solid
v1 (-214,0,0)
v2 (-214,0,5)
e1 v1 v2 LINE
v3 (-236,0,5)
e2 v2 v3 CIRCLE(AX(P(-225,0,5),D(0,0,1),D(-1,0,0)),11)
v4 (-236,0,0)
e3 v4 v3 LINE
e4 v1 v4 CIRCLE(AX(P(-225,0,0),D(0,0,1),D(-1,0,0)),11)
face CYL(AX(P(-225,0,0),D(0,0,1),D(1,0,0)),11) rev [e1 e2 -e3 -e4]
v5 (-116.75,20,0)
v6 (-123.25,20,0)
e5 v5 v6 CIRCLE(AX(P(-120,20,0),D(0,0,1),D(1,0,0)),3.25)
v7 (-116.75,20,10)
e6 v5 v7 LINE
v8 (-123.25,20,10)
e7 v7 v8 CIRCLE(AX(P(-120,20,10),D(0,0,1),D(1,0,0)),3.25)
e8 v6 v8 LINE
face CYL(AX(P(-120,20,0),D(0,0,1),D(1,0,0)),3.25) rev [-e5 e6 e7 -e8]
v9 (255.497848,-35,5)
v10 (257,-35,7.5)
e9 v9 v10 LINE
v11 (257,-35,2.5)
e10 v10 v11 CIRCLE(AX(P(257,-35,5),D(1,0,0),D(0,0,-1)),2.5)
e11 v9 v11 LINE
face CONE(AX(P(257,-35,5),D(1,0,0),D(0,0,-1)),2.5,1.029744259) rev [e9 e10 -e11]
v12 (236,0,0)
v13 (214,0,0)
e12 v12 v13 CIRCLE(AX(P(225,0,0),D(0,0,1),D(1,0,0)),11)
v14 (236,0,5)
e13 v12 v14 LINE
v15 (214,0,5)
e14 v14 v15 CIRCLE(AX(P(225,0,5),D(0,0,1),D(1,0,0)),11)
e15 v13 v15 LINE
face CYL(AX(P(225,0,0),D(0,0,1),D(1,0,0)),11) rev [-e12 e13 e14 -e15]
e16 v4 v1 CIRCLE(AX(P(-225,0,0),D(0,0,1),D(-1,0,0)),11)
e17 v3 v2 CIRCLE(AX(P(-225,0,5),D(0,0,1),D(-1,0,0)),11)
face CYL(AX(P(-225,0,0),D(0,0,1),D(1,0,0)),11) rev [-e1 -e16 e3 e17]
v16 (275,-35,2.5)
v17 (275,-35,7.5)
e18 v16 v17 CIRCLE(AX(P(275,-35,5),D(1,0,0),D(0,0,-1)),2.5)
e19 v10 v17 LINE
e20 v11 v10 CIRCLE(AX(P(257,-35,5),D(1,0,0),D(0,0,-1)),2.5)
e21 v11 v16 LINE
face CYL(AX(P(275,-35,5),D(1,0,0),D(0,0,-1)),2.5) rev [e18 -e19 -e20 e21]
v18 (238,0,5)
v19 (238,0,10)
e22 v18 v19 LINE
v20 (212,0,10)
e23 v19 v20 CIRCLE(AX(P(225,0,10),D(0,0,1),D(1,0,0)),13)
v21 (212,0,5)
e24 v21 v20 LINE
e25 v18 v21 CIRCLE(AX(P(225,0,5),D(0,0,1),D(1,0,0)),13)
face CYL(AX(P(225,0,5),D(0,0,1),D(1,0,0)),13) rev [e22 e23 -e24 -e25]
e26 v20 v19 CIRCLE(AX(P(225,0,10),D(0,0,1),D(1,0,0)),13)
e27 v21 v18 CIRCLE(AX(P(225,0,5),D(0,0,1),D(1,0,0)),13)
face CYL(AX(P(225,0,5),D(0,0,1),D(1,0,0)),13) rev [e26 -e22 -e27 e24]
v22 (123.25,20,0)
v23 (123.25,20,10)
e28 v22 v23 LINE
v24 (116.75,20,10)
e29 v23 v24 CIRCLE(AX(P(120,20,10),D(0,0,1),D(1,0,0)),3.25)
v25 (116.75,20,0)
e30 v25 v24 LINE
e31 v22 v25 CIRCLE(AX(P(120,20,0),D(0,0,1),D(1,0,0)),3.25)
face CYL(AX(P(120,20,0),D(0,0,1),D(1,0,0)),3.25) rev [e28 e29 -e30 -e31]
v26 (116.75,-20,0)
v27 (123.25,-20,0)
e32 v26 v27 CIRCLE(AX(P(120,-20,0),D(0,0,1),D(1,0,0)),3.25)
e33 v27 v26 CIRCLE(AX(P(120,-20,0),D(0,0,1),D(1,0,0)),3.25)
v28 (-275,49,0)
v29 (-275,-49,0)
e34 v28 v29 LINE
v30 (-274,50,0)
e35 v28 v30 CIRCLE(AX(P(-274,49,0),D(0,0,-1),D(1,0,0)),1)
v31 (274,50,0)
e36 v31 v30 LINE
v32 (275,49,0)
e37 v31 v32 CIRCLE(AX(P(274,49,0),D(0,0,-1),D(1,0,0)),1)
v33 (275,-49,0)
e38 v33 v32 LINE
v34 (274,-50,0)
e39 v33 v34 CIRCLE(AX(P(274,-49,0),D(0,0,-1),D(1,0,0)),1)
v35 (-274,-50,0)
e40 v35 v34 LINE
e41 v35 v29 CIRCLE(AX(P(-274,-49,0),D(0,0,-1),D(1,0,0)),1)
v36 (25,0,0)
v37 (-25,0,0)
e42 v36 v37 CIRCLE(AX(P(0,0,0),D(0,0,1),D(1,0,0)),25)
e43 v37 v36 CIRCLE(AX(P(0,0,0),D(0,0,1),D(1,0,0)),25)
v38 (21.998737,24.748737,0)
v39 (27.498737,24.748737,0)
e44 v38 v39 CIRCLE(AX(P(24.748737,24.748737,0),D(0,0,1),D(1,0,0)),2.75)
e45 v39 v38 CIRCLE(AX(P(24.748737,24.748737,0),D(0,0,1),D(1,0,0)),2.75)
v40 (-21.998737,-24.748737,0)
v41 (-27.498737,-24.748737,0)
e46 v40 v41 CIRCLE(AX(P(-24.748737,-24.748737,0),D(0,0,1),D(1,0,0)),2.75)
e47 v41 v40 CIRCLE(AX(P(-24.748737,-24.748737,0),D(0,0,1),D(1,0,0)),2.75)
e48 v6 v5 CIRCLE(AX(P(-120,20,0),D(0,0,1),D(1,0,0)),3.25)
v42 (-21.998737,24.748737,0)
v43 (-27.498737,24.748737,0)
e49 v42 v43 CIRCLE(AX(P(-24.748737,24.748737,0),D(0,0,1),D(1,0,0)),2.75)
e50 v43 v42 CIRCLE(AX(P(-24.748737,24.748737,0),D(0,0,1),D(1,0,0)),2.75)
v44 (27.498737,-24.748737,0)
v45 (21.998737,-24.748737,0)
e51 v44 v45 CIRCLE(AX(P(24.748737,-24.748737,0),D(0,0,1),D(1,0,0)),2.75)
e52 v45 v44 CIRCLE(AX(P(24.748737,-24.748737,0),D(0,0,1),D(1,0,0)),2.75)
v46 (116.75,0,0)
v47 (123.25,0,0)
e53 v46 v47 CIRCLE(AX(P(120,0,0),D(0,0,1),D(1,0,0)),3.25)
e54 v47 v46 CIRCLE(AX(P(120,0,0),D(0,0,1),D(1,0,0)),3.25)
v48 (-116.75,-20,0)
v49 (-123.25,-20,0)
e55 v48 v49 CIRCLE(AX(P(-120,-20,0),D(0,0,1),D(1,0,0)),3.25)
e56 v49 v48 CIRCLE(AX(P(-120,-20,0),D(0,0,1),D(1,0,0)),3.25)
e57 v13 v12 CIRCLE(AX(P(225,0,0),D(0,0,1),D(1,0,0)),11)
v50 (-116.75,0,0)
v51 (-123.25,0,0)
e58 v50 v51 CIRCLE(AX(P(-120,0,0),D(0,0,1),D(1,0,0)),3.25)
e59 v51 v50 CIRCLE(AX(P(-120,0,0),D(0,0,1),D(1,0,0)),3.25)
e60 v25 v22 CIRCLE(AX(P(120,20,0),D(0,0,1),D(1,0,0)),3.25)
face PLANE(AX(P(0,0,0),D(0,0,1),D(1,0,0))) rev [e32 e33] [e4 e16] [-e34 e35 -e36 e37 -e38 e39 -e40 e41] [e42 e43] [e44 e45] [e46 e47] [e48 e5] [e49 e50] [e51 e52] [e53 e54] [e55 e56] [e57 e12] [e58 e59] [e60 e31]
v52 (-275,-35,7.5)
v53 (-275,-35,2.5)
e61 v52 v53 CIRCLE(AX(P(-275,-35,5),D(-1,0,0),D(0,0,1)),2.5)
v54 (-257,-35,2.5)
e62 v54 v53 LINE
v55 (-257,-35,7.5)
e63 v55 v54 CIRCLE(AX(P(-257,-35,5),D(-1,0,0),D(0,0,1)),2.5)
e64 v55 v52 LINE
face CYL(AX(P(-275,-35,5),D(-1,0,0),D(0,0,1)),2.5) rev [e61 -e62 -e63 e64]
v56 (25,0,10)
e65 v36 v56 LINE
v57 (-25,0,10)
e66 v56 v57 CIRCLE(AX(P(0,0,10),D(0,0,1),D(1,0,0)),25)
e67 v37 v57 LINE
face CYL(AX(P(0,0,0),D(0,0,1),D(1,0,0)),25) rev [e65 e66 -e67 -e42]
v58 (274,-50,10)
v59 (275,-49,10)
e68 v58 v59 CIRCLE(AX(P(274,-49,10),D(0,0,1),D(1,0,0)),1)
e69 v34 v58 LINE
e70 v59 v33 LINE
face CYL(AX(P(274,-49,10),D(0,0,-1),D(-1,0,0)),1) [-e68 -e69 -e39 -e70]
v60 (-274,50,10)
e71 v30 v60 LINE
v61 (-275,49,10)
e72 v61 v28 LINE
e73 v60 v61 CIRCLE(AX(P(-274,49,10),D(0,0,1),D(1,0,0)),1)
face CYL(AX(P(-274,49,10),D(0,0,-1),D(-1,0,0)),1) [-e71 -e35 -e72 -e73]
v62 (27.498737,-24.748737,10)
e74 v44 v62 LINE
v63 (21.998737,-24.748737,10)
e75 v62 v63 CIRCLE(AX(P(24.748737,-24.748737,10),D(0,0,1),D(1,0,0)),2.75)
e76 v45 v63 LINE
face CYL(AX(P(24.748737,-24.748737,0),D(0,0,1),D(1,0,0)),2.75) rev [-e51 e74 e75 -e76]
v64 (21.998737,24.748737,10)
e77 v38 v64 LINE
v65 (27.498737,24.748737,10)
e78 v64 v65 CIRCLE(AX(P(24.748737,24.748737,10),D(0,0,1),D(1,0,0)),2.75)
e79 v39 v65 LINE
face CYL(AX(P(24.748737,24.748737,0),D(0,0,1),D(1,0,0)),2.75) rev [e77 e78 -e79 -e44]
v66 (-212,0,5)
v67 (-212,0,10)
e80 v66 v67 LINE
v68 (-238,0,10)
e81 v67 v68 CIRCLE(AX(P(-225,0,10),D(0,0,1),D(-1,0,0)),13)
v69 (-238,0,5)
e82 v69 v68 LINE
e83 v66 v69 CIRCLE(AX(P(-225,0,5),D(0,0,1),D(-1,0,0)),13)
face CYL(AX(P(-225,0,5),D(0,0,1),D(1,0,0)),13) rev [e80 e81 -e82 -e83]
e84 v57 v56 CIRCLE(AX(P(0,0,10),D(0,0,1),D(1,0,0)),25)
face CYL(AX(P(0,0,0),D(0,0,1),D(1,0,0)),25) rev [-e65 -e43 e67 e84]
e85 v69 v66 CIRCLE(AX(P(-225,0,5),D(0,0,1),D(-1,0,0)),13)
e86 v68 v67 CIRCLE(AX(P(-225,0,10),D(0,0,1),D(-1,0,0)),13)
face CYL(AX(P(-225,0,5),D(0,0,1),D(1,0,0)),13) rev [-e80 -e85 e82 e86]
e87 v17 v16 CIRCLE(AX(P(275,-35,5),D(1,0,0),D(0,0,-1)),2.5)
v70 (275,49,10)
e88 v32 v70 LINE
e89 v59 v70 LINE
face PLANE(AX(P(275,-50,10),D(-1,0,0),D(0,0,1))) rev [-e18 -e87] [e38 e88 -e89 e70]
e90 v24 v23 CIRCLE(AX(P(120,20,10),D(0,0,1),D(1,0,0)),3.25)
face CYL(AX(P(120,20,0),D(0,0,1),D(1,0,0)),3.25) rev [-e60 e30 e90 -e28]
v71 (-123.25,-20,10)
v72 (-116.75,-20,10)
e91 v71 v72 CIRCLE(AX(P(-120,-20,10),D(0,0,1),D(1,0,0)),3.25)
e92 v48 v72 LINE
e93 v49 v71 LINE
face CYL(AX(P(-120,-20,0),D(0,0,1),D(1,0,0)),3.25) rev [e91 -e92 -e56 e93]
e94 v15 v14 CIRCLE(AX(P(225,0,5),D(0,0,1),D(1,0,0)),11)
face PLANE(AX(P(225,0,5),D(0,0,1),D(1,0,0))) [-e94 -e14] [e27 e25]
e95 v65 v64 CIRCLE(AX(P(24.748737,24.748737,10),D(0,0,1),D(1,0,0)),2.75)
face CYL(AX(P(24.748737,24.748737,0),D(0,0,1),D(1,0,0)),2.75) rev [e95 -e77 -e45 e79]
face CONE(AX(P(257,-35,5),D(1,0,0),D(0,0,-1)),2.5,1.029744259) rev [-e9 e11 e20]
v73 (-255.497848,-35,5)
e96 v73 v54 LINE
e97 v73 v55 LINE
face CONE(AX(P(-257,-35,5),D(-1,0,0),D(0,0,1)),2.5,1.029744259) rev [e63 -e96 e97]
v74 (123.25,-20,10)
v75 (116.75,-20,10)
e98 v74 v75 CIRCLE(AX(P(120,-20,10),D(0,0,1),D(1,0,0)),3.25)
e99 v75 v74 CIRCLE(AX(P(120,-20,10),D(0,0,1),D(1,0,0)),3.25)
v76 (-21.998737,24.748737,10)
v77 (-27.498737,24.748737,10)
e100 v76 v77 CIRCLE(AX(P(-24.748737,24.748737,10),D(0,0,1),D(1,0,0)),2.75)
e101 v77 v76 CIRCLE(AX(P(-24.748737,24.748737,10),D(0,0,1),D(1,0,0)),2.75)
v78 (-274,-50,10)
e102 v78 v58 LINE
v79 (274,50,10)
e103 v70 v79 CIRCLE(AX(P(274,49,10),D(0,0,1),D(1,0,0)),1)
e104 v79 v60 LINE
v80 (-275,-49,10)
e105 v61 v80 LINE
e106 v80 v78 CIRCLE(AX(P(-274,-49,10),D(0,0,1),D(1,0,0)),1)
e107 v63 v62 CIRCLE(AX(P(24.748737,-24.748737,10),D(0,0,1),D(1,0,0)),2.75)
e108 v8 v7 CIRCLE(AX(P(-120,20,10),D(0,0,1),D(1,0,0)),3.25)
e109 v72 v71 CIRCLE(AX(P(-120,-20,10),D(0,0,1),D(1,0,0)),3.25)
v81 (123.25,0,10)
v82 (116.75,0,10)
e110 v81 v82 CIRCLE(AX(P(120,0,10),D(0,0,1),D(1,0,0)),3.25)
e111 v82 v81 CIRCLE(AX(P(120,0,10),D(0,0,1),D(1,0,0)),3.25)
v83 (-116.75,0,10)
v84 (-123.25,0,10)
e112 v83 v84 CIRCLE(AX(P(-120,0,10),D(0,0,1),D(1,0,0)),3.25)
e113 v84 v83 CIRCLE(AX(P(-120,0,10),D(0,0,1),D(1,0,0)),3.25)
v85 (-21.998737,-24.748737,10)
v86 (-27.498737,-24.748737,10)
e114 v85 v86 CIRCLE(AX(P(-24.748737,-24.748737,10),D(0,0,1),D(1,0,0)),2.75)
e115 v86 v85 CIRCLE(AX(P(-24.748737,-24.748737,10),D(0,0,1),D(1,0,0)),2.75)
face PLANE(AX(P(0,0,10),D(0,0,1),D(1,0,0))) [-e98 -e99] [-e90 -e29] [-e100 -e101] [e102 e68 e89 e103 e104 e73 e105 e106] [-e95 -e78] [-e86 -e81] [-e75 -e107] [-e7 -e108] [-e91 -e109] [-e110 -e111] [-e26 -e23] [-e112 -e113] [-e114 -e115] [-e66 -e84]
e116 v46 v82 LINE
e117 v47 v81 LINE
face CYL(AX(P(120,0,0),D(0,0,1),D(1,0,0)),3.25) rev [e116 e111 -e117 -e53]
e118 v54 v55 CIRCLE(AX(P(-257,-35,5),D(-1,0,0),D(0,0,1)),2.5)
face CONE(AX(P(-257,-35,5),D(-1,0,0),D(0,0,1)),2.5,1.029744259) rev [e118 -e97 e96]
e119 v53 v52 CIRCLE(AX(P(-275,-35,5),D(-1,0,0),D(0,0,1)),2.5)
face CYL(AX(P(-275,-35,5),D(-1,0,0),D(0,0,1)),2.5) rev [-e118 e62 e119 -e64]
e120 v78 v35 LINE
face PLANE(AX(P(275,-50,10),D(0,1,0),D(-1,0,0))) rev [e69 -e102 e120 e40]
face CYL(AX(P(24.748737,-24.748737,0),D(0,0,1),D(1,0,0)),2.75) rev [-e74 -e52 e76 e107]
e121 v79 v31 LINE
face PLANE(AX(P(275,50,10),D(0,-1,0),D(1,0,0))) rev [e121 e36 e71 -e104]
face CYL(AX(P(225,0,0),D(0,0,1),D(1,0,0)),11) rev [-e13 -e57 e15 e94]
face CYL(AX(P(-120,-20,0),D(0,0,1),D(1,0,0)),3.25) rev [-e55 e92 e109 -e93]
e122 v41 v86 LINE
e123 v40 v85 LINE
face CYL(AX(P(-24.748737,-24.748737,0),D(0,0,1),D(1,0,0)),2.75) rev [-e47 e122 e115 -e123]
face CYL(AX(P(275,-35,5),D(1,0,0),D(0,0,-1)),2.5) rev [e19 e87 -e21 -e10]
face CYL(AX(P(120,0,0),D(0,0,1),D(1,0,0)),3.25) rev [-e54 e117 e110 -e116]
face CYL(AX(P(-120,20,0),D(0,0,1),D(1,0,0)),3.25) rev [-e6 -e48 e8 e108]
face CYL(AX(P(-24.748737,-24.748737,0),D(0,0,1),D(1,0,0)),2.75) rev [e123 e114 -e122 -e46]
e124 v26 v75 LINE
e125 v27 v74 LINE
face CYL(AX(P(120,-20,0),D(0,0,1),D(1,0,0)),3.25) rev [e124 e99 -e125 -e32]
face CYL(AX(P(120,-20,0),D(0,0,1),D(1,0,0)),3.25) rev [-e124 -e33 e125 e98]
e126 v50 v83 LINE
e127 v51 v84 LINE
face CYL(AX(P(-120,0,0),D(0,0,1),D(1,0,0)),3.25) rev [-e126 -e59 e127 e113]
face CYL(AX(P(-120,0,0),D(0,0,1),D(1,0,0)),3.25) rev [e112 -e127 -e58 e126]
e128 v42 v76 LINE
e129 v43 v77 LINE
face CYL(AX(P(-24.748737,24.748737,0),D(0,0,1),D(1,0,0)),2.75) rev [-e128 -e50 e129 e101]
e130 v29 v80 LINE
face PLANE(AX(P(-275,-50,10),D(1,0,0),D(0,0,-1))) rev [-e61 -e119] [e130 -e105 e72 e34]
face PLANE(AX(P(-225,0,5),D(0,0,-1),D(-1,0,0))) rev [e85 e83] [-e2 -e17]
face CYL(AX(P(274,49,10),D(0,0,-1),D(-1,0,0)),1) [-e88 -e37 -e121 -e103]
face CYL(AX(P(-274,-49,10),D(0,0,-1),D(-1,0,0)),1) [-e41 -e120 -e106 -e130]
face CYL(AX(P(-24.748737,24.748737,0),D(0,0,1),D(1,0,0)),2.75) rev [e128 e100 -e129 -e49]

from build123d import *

# Parameters (mm, degrees)
SKETCH1_W           = 550
SKETCH1_H           = 100
BOSS_EXTRUDE1_DEPTH = 10
SKETCH3_R           = 13
CUT_EXTRUDE2_DEPTH  = 5
SKETCH4_R           = 11
CUT_EXTRUDE3_DEPTH  = 280.55321497
SKETCH5_R           = 25
CUT_EXTRUDE4_DEPTH  = 280.687325419
SKETCH6_R           = 2.75
CUT_EXTRUDE5_DEPTH  = 280.687325419
SKETCH7_R           = 3.25
CUT_EXTRUDE6_DEPTH  = 280.687325419
FILLET1_R           = 1


with BuildPart() as part:
    # Sketch1 → Boss-Extrude1 (new body)
    with BuildSketch(Plane.XY):
        Rectangle(SKETCH1_W, SKETCH1_H)
    extrude(amount=BOSS_EXTRUDE1_DEPTH)

    # Sketch3 → Cut-Extrude2 (cut)
    with BuildSketch(Plane.XY.offset(10)):
        with Locations((225, 0)):
            Circle(SKETCH3_R)
        with Locations(Location((-225, 0, 0), (0, 0, 180))):
            Circle(SKETCH3_R)
    extrude(amount=-CUT_EXTRUDE2_DEPTH, mode=Mode.SUBTRACT)

    # Sketch4 → Cut-Extrude3 (cut, through all)
    with BuildSketch(Plane.XY.offset(5)):
        with Locations((225, 0)):
            Circle(SKETCH4_R)
        with Locations(Location((-225, 0, 0), (0, 0, 180))):
            Circle(SKETCH4_R)
    extrude(amount=-CUT_EXTRUDE3_DEPTH, mode=Mode.SUBTRACT)

    # Sketch5 → Cut-Extrude4 (cut, through all)
    with BuildSketch(Plane.XY.offset(10)):
        Circle(SKETCH5_R)
    extrude(amount=-CUT_EXTRUDE4_DEPTH, mode=Mode.SUBTRACT)

    # Sketch6 → Cut-Extrude5 (cut, through all)
    with BuildSketch(Plane.XY.offset(10)):
        with Locations((-24.748737342, 24.748737342)):
            Circle(SKETCH6_R)
        with Locations((24.748737342, 24.748737342)):
            Circle(SKETCH6_R)
        with Locations((24.748737342, -24.748737342)):
            Circle(SKETCH6_R)
        with Locations((-24.748737342, -24.748737342)):
            Circle(SKETCH6_R)
    extrude(amount=-CUT_EXTRUDE5_DEPTH, mode=Mode.SUBTRACT)

    # Sketch7 → Cut-Extrude6 (cut, through all)
    with BuildSketch(Plane.XY.offset(10)):
        with Locations((-120, -20)):
            Circle(SKETCH7_R)
        with Locations((120, -20)):
            Circle(SKETCH7_R)
        with Locations((120, 20)):
            Circle(SKETCH7_R)
        with Locations((-120, 20)):
            Circle(SKETCH7_R)
        with Locations((-120, 0)):
            Circle(SKETCH7_R)
        with Locations((120, 0)):
            Circle(SKETCH7_R)
    extrude(amount=-CUT_EXTRUDE6_DEPTH, mode=Mode.SUBTRACT)

    # Fillet1
    fillet1_edges = [part.edges().sort_by_distance(p)[0] for p in [
        (-275, 50, 5),
        (275, 50, 5),
        (275, -50, 5),
        (-275, -50, 5),
    ]]
    fillet(fillet1_edges, radius=FILLET1_R)

    # Sketch9 → M6 Tapped Hole1 (revolve, cut)
    with BuildSketch(Plane(origin=(-275, -35, 5), x_dir=(0, 0, 1), z_dir=(0, 1, 0))):
        Polygon((0, 0), (0, 19.502151548), (2.5, 18), (2.5, 0), align=None)
    m6_tapped_hole1 = revolve(axis=Axis((-281.35, -35, 5), (1, 0, 0)), mode=Mode.SUBTRACT)

    # Mirror1: M6 Tapped Hole1 across plane
    add(m6_tapped_hole1.mirror(Plane(origin=(0, 0, 0), x_dir=(0, 0, 1), z_dir=(1, 0, 0))), mode=Mode.SUBTRACT)


solid = part.part
